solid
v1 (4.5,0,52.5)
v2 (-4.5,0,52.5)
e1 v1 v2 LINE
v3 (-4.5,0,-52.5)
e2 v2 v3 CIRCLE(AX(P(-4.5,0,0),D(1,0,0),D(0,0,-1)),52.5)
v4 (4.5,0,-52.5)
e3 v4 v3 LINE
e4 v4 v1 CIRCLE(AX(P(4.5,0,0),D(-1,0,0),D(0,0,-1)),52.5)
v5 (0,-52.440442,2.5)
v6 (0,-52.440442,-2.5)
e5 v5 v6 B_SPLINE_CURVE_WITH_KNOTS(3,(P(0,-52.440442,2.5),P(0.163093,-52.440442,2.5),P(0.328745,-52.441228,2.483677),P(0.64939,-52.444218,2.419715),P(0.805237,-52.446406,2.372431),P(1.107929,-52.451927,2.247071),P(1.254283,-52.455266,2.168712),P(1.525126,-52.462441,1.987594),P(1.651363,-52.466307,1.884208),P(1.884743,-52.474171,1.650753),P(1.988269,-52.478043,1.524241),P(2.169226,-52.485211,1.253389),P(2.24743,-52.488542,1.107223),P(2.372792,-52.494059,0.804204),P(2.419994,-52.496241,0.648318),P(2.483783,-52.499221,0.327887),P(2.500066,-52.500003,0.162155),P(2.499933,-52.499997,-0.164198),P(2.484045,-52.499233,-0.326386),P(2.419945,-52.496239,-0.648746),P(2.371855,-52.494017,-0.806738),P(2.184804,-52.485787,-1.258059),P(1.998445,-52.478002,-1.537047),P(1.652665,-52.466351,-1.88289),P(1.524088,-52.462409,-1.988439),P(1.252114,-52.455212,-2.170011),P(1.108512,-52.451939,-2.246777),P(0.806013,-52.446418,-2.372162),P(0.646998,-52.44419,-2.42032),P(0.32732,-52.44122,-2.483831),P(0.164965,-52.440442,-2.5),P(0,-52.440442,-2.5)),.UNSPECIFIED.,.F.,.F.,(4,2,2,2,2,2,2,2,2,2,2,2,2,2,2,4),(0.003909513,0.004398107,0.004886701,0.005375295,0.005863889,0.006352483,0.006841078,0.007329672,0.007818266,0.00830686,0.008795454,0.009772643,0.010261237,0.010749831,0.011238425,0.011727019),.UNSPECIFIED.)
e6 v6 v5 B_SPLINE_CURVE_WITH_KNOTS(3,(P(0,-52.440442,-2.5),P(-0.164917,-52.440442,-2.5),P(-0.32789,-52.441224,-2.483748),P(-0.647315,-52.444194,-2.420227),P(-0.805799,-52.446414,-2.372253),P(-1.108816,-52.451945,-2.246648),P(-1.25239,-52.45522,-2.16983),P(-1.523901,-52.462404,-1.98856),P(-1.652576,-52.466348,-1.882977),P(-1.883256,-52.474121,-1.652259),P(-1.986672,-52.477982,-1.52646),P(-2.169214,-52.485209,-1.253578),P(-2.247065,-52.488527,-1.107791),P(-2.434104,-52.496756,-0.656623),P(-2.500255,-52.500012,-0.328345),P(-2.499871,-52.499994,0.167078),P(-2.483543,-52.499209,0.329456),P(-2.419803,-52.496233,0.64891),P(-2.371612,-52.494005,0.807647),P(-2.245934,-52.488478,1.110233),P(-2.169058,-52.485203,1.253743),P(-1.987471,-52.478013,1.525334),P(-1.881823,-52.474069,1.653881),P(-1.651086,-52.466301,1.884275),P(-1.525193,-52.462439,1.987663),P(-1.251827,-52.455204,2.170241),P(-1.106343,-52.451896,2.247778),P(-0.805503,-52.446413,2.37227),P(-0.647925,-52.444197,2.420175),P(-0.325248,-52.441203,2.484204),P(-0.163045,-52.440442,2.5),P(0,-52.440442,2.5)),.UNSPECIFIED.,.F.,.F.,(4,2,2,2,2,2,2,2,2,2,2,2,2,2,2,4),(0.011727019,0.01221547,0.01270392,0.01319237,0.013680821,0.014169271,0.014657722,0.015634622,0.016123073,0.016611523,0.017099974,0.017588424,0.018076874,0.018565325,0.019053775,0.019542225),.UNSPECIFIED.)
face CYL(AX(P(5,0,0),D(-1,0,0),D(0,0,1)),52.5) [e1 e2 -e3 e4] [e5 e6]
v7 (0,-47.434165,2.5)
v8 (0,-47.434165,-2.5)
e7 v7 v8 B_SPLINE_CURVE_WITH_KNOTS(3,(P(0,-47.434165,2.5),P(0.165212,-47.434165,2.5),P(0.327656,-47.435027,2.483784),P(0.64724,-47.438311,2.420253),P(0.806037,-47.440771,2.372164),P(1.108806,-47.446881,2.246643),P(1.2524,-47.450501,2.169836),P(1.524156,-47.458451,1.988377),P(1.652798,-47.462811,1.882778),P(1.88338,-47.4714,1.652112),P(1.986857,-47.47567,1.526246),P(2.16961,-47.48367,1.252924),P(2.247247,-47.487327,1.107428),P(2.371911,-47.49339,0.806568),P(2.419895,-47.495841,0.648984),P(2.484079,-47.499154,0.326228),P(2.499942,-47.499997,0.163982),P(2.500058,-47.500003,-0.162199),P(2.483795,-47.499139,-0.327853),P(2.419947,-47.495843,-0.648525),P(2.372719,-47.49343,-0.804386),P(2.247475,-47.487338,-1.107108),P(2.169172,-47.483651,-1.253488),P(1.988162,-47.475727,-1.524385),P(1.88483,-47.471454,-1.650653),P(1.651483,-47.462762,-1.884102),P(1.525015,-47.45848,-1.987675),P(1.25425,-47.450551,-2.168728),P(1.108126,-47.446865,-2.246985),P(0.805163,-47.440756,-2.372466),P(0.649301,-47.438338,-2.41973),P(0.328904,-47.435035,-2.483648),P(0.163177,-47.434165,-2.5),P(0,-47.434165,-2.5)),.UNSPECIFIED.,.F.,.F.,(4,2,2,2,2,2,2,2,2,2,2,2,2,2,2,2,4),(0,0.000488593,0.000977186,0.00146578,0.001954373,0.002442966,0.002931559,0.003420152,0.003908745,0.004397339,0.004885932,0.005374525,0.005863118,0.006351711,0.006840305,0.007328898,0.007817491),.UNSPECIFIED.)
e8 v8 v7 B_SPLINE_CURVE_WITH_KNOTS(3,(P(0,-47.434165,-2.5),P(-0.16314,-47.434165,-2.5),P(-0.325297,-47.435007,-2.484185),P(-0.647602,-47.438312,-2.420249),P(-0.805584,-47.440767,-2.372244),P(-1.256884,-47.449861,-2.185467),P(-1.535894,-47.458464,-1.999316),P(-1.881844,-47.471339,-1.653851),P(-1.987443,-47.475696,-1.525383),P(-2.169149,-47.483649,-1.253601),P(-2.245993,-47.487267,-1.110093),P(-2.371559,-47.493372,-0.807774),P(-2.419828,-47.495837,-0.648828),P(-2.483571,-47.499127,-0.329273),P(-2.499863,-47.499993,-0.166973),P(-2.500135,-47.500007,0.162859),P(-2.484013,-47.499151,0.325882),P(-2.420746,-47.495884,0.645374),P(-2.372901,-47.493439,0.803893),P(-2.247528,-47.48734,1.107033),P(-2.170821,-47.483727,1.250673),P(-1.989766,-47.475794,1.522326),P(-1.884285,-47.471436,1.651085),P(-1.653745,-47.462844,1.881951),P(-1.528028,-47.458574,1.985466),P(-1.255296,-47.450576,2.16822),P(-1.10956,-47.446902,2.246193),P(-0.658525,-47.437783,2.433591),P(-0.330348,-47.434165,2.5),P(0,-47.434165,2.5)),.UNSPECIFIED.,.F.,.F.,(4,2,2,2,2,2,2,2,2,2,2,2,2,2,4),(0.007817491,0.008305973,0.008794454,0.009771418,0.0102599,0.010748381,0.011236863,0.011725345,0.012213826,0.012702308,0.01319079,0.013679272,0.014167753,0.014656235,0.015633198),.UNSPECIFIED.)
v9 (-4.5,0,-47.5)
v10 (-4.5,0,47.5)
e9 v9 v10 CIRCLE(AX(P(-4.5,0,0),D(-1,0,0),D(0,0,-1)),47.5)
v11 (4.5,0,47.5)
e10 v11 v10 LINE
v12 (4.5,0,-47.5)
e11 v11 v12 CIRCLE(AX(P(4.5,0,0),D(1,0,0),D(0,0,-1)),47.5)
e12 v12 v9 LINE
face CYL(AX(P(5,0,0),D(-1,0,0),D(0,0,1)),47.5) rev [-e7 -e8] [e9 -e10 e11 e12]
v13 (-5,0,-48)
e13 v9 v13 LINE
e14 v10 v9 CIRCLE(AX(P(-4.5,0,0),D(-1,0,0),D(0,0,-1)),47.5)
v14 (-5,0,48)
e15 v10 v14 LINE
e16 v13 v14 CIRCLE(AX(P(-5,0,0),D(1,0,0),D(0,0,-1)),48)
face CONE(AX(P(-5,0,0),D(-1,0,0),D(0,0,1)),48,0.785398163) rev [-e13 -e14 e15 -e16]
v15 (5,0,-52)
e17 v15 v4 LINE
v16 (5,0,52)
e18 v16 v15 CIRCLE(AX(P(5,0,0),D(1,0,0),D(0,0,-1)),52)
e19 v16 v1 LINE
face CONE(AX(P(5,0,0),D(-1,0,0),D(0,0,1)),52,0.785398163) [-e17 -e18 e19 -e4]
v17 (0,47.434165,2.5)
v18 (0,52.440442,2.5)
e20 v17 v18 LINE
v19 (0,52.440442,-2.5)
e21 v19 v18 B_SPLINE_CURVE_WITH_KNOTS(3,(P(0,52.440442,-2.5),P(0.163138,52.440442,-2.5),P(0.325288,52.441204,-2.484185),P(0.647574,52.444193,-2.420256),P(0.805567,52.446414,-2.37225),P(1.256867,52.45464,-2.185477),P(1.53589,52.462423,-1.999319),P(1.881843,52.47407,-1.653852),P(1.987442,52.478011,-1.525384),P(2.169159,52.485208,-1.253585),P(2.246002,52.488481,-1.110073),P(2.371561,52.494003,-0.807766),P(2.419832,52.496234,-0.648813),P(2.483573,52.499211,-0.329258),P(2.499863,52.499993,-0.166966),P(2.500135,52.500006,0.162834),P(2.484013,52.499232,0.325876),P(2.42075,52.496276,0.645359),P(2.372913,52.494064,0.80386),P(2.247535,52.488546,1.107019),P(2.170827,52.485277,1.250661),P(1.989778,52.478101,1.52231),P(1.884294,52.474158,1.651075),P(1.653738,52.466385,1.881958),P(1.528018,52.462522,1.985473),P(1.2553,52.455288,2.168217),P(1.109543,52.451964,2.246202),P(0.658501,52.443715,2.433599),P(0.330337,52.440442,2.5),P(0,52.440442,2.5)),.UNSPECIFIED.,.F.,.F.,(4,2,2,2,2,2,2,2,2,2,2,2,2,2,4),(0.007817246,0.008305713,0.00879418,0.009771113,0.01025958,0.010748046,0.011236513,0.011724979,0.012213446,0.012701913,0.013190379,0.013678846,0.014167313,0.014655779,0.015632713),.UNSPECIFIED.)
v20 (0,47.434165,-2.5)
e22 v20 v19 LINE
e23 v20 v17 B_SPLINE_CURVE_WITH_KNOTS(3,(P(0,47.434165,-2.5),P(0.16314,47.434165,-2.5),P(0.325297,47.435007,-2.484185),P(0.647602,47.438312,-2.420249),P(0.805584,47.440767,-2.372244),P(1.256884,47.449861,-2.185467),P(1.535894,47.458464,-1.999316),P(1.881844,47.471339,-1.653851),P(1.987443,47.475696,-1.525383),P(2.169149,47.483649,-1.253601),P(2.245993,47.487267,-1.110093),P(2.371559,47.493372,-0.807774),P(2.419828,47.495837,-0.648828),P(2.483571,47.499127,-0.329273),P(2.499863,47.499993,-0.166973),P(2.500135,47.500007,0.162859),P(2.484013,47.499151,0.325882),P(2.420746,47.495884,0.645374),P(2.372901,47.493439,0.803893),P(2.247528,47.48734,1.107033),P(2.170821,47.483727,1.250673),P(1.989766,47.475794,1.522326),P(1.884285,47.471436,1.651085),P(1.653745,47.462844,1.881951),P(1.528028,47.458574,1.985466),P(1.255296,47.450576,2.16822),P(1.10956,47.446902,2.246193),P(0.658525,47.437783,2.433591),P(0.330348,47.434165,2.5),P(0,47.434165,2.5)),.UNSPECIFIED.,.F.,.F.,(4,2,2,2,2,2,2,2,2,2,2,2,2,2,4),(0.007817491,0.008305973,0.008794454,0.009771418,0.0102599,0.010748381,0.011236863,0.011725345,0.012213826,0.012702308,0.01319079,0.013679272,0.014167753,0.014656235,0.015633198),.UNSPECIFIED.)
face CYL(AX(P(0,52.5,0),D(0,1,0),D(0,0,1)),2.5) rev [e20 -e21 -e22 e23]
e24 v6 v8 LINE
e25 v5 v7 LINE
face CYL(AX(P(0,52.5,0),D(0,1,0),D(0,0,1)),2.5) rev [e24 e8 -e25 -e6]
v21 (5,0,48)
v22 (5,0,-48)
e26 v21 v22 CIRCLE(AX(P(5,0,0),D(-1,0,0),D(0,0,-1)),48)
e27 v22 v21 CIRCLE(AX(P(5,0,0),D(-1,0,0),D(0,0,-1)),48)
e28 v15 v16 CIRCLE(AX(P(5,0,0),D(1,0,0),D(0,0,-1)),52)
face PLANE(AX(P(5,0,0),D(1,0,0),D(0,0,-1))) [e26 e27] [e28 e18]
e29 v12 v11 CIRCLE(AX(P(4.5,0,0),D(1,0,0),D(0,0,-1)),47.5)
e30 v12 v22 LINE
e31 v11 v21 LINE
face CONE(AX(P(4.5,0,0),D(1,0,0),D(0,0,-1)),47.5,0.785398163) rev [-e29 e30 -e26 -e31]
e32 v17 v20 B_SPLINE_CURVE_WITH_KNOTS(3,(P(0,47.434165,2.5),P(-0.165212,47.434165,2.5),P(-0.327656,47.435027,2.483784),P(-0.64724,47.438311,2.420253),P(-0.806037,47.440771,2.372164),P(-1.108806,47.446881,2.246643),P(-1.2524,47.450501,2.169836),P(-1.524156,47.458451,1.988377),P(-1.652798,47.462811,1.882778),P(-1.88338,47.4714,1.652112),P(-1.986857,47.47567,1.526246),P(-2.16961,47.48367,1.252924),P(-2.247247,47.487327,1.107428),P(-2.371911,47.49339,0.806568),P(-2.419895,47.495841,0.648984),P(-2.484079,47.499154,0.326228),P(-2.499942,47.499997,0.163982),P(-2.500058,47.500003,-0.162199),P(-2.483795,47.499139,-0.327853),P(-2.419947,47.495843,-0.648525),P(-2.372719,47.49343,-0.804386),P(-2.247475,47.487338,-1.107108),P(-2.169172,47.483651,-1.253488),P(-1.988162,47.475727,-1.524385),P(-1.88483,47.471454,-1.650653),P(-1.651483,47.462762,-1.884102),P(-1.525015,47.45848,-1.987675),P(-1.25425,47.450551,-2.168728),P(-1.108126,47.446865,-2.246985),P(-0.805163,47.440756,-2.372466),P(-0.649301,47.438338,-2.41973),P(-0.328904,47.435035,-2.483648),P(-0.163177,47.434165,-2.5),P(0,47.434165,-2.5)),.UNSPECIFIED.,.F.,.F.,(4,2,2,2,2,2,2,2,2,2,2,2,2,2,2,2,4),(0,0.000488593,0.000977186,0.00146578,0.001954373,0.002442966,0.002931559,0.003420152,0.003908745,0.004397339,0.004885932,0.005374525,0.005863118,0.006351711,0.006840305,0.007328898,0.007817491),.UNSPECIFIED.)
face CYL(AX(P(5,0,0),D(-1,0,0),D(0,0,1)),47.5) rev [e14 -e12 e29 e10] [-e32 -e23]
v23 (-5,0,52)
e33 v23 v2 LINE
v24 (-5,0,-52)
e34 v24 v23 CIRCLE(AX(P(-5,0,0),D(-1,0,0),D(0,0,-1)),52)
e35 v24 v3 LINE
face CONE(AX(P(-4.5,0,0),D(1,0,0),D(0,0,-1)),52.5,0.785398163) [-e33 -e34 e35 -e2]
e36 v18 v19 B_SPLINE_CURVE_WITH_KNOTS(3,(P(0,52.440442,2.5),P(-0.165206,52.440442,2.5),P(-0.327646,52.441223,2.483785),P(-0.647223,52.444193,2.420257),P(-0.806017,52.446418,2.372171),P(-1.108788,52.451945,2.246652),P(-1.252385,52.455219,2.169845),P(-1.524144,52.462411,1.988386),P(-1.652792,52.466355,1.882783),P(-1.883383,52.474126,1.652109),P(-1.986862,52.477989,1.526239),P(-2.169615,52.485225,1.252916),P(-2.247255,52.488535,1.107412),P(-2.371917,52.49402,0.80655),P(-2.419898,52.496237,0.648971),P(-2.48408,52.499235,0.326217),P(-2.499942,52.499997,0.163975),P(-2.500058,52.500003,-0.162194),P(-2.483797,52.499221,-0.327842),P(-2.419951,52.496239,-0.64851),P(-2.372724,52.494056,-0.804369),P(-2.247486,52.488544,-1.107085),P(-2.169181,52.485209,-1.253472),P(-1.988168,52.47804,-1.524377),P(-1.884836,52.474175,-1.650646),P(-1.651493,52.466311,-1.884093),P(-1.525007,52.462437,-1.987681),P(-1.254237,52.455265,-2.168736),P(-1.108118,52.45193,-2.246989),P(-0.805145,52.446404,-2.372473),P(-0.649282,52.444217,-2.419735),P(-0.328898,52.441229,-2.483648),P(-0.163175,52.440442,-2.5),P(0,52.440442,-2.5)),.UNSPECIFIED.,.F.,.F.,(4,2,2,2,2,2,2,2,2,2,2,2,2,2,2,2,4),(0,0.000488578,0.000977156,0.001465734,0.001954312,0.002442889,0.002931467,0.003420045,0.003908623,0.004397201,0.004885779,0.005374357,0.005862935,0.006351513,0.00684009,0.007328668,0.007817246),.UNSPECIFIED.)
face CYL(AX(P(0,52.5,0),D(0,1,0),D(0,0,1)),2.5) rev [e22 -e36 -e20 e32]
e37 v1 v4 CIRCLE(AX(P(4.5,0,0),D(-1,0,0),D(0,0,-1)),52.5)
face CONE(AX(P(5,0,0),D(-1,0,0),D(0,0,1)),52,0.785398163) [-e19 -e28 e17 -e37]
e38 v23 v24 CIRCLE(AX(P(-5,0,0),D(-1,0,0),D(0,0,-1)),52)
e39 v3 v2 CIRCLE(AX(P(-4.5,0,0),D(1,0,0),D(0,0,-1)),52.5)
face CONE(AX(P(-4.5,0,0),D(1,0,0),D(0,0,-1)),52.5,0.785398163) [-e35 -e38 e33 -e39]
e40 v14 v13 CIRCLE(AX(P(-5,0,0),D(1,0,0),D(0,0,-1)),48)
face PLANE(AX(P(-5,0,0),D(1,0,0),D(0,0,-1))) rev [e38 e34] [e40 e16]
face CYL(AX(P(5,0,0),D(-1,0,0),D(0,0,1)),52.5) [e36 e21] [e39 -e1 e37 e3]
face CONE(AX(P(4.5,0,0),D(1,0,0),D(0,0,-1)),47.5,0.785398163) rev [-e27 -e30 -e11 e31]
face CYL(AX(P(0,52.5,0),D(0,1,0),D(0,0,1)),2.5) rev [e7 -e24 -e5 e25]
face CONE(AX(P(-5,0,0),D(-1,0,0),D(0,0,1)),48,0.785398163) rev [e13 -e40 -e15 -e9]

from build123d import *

# Parameters (mm, degrees)
SKETCH_1_R         = 52.5
SKETCH_1_R_2       = 47.5
EXTRUDE_1_DEPTH    = 5
CHAMFER_1_SIZE     = 0.5
HOLE_WIZARD_M6_1_D = 5


with BuildPart() as part:
    # 草图1 → 凸台-拉伸1 (new, symmetric)
    with BuildSketch(Plane(origin=(0, 0, 0), x_dir=(0, 0, -1), z_dir=(1, 0, 0))):
        Circle(SKETCH_1_R)
        Circle(SKETCH_1_R_2, mode=Mode.SUBTRACT)
    extrude(amount=EXTRUDE_1_DEPTH, both=True)

    # 倒角1
    chamfer_1_edges = [part.edges().sort_by_distance(p)[0] for p in [
        (-5, 0, 52.5),
        (5, 0, 52.5),
        (-5, 0, 47.5),
        (5, 0, 47.5),
    ]]
    chamfer(chamfer_1_edges, length=CHAMFER_1_SIZE)

    # M6 螺纹孔1 (through all)
    with Locations(Plane(origin=(0, 52.5, 0), x_dir=(1, 0, 0), z_dir=(0, 1, 0))):
        with Locations((0, 0)):
            Hole(HOLE_WIZARD_M6_1_D / 2)


solid = part.part
